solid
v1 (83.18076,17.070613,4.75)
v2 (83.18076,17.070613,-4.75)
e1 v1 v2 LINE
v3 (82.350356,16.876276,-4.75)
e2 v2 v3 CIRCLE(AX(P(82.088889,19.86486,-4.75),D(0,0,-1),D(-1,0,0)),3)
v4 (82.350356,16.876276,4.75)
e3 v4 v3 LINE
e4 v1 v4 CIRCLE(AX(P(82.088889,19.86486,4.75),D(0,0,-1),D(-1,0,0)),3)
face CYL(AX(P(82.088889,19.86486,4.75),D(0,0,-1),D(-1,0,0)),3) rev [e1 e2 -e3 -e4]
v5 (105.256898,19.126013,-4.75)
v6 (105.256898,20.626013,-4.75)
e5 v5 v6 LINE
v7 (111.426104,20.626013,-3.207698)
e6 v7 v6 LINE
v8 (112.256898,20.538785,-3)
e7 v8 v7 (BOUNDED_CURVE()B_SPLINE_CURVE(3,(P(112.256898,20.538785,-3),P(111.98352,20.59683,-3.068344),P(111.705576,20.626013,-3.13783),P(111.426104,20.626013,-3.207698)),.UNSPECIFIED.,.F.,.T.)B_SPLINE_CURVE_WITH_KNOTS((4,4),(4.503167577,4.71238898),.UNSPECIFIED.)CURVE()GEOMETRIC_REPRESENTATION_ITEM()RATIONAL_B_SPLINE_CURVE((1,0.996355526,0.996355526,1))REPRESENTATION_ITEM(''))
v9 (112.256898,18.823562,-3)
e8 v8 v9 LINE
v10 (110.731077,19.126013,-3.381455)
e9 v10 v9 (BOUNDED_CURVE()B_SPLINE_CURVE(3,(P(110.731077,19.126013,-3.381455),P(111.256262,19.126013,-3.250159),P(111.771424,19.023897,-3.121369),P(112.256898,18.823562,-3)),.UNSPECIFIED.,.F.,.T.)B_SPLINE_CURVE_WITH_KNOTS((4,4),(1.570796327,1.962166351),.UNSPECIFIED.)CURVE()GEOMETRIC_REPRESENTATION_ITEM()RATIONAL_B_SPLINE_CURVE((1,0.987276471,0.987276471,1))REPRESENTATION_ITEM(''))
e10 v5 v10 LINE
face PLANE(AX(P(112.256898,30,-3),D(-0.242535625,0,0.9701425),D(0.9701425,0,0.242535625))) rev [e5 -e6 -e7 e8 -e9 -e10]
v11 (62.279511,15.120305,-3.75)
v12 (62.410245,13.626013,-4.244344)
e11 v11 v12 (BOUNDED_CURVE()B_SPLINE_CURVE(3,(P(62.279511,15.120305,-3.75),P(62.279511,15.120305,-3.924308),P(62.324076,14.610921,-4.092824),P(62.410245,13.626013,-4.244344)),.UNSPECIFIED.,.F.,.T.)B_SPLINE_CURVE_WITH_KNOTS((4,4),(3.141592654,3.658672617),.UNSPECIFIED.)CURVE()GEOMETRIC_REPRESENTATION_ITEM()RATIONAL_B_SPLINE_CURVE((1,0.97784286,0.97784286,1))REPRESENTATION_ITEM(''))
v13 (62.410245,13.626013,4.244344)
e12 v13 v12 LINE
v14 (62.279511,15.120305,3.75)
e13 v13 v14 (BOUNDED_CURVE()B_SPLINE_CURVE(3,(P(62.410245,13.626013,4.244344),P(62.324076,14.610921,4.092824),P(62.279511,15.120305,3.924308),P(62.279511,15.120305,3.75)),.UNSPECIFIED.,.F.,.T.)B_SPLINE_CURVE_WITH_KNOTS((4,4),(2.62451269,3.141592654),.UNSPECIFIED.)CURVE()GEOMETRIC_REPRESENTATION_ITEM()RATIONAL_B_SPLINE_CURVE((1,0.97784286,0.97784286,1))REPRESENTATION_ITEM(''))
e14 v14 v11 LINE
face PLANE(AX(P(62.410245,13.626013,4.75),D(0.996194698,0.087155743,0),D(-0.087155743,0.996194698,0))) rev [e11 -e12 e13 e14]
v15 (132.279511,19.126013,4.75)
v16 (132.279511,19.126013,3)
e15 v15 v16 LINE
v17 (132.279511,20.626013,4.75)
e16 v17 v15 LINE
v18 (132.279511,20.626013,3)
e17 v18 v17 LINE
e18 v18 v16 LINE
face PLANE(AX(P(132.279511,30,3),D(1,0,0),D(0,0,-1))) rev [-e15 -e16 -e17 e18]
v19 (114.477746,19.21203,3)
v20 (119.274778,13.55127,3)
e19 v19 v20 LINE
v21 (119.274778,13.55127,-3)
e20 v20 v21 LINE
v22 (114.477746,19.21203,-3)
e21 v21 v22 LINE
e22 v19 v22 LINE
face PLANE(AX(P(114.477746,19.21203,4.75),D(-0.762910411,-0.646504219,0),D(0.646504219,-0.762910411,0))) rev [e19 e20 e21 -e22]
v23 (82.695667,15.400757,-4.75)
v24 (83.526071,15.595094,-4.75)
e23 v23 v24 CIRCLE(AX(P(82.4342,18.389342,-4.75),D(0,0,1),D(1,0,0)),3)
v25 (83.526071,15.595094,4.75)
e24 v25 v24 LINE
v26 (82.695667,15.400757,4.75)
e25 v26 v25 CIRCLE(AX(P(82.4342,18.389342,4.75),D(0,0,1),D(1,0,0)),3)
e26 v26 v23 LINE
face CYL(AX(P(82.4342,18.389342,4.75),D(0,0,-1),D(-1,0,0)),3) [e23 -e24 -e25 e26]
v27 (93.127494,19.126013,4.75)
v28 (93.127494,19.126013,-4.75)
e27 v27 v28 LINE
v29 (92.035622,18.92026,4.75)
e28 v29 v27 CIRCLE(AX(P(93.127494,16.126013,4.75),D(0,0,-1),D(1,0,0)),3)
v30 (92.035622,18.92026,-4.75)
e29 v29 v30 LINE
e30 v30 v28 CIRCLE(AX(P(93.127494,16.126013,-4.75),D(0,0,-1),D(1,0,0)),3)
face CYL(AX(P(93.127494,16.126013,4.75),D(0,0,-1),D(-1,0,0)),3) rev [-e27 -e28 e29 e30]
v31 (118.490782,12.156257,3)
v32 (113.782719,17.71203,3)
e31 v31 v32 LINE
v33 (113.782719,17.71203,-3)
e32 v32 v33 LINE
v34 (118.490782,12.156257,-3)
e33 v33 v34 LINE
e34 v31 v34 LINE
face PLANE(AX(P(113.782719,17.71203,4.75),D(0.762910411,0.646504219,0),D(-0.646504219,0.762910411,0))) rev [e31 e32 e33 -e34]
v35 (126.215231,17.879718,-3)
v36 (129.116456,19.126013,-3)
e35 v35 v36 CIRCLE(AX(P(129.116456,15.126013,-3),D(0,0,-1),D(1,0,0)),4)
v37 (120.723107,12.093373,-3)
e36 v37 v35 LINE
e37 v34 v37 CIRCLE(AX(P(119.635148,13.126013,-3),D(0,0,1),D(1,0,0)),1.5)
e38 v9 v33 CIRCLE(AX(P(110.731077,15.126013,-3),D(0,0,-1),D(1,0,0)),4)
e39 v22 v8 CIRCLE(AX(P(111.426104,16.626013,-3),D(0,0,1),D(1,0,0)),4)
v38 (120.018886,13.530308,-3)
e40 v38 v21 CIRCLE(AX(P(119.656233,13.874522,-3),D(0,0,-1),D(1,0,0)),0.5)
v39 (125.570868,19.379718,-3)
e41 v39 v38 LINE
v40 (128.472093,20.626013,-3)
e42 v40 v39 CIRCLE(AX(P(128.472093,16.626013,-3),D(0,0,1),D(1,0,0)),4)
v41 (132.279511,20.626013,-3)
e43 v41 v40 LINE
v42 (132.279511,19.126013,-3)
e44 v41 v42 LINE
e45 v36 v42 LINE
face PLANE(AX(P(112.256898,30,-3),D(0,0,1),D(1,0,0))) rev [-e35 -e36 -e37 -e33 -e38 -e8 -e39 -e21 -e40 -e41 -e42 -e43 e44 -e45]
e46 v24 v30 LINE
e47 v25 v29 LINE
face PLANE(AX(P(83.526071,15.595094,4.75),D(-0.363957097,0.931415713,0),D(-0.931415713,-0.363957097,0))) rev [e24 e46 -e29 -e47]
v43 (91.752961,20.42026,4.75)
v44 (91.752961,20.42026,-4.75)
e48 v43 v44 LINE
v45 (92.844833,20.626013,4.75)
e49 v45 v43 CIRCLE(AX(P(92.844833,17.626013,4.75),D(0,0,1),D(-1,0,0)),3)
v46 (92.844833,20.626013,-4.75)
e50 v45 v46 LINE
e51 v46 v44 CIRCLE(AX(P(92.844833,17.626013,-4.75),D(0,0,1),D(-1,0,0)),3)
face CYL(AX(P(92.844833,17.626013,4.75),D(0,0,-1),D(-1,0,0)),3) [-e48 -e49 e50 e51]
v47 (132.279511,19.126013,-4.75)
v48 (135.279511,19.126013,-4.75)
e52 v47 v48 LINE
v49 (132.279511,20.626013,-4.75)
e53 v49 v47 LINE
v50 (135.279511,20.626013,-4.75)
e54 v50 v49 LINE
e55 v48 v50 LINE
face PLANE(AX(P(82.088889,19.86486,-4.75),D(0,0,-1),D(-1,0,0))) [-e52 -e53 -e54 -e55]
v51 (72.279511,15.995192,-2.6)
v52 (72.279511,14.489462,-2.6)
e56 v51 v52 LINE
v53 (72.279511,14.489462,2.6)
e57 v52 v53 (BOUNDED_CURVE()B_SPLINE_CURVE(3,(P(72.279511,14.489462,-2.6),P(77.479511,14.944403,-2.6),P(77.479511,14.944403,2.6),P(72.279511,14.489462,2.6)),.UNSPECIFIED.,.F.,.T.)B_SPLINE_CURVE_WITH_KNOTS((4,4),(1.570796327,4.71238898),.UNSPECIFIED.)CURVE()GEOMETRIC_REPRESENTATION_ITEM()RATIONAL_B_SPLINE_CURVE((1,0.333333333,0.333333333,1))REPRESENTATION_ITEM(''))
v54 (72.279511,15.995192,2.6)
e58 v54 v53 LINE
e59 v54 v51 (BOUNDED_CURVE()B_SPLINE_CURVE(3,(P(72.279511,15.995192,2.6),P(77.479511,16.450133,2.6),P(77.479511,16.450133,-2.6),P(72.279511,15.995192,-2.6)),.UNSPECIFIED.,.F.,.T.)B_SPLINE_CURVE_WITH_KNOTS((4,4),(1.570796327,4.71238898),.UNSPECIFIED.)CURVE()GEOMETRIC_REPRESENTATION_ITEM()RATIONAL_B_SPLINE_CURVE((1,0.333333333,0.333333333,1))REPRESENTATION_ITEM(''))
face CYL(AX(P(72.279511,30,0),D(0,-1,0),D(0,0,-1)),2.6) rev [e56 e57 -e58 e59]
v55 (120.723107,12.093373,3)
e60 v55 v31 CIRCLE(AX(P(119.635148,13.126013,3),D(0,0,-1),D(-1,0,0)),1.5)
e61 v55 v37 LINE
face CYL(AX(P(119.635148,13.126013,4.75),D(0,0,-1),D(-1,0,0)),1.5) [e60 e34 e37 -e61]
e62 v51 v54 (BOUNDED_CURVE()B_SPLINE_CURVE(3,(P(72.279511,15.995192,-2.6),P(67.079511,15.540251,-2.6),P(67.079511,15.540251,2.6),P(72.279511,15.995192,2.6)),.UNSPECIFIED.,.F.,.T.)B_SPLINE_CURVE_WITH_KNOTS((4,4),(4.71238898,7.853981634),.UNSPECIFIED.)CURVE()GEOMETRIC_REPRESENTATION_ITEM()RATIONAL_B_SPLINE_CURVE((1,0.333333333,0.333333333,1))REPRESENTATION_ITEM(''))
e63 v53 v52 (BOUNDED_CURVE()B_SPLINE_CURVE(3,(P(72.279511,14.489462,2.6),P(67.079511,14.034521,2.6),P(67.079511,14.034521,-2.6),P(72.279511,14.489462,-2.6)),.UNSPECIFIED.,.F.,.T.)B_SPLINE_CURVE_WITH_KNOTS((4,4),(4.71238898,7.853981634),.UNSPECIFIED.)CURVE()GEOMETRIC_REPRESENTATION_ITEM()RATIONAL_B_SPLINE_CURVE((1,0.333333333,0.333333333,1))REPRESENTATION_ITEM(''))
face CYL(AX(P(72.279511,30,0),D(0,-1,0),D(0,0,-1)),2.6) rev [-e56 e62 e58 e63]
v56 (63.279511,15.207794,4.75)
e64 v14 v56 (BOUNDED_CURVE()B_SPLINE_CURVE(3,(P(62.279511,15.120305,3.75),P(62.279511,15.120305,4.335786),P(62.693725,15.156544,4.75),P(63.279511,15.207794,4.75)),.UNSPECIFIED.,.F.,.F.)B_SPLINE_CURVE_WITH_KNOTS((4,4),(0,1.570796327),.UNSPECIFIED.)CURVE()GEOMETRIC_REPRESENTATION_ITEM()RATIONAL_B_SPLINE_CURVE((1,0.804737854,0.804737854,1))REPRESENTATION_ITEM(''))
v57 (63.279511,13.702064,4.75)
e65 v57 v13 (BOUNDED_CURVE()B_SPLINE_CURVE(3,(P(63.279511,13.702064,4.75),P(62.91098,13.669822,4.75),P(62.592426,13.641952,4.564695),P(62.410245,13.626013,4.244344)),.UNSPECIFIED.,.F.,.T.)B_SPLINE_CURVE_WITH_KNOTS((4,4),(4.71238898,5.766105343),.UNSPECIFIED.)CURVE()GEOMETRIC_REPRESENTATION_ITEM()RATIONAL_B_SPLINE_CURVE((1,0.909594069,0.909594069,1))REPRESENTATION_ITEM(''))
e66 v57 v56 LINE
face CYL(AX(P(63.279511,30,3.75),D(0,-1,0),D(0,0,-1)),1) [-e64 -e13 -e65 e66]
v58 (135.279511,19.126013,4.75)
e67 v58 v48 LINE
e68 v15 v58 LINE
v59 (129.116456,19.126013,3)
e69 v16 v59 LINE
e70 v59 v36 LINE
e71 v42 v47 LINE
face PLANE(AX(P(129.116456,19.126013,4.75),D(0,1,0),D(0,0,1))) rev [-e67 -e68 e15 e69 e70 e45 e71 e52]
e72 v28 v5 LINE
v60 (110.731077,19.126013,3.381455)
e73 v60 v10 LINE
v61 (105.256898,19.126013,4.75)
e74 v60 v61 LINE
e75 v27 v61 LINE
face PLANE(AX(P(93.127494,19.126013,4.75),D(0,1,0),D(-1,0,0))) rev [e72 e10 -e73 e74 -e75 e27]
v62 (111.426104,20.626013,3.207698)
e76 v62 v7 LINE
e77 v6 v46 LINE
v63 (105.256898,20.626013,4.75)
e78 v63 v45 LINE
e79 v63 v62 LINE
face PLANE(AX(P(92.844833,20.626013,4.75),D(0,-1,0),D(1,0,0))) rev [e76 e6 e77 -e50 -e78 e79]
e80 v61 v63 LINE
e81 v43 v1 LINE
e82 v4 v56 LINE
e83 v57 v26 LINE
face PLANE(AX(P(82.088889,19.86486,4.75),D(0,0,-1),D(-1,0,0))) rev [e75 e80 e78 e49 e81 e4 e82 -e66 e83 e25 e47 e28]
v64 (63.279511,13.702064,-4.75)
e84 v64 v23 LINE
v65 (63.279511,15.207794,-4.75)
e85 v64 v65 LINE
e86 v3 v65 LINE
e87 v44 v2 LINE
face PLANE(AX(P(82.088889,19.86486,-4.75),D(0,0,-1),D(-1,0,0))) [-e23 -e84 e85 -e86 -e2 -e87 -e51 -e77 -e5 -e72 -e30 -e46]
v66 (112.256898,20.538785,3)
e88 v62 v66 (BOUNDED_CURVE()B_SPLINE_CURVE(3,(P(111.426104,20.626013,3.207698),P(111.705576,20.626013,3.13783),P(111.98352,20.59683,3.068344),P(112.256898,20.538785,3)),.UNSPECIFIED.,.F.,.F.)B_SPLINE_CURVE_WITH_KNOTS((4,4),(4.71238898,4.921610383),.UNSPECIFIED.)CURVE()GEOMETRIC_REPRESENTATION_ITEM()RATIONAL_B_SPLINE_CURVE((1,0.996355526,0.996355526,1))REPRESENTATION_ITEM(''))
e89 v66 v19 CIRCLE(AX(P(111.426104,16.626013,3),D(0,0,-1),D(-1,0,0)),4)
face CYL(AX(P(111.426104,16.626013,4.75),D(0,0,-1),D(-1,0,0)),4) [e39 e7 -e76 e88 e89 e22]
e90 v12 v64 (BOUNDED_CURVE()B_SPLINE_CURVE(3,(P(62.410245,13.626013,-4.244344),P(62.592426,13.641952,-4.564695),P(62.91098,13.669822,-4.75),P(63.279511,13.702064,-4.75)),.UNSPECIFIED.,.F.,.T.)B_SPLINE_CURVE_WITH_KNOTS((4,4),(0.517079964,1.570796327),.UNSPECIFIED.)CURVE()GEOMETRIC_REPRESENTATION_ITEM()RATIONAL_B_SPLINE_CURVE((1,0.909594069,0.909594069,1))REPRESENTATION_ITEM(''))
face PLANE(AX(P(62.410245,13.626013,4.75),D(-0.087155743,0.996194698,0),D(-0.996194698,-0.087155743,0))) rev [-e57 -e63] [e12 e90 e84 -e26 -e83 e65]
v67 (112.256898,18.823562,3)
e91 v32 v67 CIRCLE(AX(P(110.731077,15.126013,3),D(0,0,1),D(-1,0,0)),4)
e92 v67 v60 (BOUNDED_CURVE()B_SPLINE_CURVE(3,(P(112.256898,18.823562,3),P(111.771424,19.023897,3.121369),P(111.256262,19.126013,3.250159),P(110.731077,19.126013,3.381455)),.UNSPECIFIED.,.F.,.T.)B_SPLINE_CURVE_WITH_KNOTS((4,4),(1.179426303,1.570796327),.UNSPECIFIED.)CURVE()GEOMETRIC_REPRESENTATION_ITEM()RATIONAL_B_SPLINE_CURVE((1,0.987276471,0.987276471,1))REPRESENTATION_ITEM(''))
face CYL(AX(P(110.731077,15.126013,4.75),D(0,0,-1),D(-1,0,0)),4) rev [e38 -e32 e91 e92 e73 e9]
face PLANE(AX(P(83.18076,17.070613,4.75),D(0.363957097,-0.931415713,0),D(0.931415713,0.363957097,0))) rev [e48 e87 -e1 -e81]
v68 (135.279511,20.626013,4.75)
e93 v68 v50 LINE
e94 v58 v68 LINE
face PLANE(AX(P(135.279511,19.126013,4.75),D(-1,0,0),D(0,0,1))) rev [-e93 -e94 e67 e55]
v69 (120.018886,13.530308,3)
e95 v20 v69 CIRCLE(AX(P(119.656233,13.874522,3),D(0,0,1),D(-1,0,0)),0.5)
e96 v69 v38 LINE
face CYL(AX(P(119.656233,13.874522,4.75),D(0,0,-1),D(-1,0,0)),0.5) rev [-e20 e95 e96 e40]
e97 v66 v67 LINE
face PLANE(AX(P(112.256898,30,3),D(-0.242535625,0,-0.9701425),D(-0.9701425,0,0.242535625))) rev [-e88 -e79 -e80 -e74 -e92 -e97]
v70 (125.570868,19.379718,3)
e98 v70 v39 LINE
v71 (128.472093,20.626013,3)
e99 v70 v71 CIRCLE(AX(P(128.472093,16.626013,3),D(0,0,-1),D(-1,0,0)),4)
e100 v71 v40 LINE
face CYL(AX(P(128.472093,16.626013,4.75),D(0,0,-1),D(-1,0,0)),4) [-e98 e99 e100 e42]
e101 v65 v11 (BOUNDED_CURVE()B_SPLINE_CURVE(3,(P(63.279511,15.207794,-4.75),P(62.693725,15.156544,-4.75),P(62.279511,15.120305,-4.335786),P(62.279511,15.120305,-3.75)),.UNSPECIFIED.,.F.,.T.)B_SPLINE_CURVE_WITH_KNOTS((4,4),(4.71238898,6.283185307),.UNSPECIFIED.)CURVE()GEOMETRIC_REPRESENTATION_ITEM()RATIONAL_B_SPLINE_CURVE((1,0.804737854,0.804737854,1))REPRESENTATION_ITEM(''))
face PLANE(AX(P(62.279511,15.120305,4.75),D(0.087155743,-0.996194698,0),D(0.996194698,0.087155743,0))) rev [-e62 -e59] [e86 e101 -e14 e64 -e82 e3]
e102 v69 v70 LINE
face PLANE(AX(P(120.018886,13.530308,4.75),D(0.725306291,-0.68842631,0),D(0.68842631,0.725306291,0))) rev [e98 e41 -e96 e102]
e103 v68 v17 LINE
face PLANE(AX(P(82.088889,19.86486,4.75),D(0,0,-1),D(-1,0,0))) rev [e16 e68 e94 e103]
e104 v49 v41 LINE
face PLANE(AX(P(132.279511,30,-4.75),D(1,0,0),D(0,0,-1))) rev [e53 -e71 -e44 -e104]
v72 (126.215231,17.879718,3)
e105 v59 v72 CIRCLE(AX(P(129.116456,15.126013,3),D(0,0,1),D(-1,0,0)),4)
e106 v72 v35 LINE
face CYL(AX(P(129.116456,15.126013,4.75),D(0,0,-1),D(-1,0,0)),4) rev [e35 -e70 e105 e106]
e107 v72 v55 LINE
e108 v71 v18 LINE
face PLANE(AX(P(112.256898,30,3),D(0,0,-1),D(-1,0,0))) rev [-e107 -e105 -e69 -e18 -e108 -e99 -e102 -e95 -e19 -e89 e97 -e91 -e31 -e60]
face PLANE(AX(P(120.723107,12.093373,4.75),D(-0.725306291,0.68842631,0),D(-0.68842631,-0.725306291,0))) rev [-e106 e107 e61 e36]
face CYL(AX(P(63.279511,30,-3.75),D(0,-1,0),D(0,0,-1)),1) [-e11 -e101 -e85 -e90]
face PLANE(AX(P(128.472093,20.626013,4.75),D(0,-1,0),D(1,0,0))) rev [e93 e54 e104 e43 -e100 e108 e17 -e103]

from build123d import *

# Parameters (mm, degrees)
BOSS_EXTRUDE1_DEPTH = 4.75
SKETCH2_OUTSIDE_W   = 89.832
SKETCH2_OUTSIDE_H   = 26.332
SKETCH2_OUTSIDE_R   = 2.6
CUT_EXTRUDE1_DEPTH  = 30


with BuildPart() as part:
    # Sketch1 → Boss-Extrude1 (new, symmetric)
    with BuildSketch(Plane.XY):
        with BuildLine():
            Line((128.472093399, 20.626012941), (135.279511004, 20.626012941))
            Line((135.279511004, 20.626012941), (135.279511004, 19.126012941))
            Line((135.279511004, 19.126012941), (129.116456396, 19.126012941))
            ThreePointArc((129.116456396, 19.126012941), (127.537662704, 18.801255856), (126.215231232, 17.879718181))
            Line((126.215231232, 17.879718181), (120.723107444, 12.093373476))
            ThreePointArc((120.723107444, 12.093373476), (119.592910743, 11.626607721), (118.490782391, 12.156256613))
            Line((118.490782391, 12.156256613), (113.782718692, 17.712029816))
            ThreePointArc((113.782718692, 17.712029816), (112.412732854, 18.755342597), (110.731077047, 19.126012941))
            Line((110.731077047, 19.126012941), (93.127493614, 19.126012941))
            ThreePointArc((93.127493614, 19.126012941), (92.571949476, 19.074126018), (92.035622322, 18.920260082))
            Line((92.035622322, 18.920260082), (83.526071058, 15.595094388))
            ThreePointArc((83.526071058, 15.595094388), (83.117810035, 15.468266897), (82.695666994, 15.400757434))
            Line((82.695666994, 15.400757434), (62.410244618, 13.626012941))
            Line((62.410244618, 13.626012941), (62.279511004, 15.120304988))
            Line((62.279511004, 15.120304988), (82.350355756, 16.876276372))
            ThreePointArc((82.350355756, 16.876276372), (82.772498797, 16.943785835), (83.180759819, 17.070613325))
            Line((83.180759819, 17.070613325), (91.752961452, 20.420260082))
            ThreePointArc((91.752961452, 20.420260082), (92.289288606, 20.574126018), (92.844832744, 20.626012941))
            Line((92.844832744, 20.626012941), (111.42610449, 20.626012941))
            ThreePointArc((111.42610449, 20.626012941), (113.107760296, 20.255342597), (114.477746134, 19.212029816))
            Line((114.477746134, 19.212029816), (119.274777803, 13.551269534))
            ThreePointArc((119.274777803, 13.551269534), (119.64215392, 13.374719903), (120.018886154, 13.530308488))
            Line((120.018886154, 13.530308488), (125.570868236, 19.379718181))
            ThreePointArc((125.570868236, 19.379718181), (126.893299708, 20.301255856), (128.472093399, 20.626012941))
        make_face()
    extrude(amount=BOSS_EXTRUDE1_DEPTH, both=True)

    # Sketch2 outside → Cut-Extrude1 (cut)
    # profile 1 of 2: a face of its own
    with BuildSketch(Plane(origin=(0, 0, 0), x_dir=(1, 0, 0), z_dir=(0, 1, 0))):
        with Locations((98.78, 0)):
            Rectangle(SKETCH2_OUTSIDE_W, SKETCH2_OUTSIDE_H)
        with BuildLine():
            Line((132.279511004, 4.75), (132.279511004, 3))
            Line((132.279511004, 3), (112.256897869, 3))
            Line((112.256897869, 3), (105.256897869, 4.75))
            Line((105.256897869, 4.75), (63.279511004, 4.75))
            ThreePointArc((63.279511004, 4.75), (62.572404223, 4.457106781), (62.279511004, 3.75))
            Line((62.279511004, 3.75), (62.279511004, -3.75))
            ThreePointArc((62.279511004, -3.75), (62.572404223, -4.457106781), (63.279511004, -4.75))
            Line((63.279511004, -4.75), (105.256897869, -4.75))
            Line((105.256897869, -4.75), (112.256897869, -3))
            Line((112.256897869, -3), (132.279511004, -3))
            Line((132.279511004, -3), (132.279511004, -4.75))
            Line((132.279511004, -4.75), (135.279511004, -4.75))
            Line((135.279511004, -4.75), (135.279511004, 4.75))
            Line((135.279511004, 4.75), (132.279511004, 4.75))
        make_face(mode=Mode.SUBTRACT)
    # profile 2 of 2: a face of its own
    with BuildSketch(Plane(origin=(0, 0, 0), x_dir=(1, 0, 0), z_dir=(0, 1, 0))):
        with Locations(Location((72.279511004, 0, 0), (0, 0, 180))):
            Circle(SKETCH2_OUTSIDE_R)
    extrude(amount=CUT_EXTRUDE1_DEPTH, mode=Mode.SUBTRACT)


solid = part.part
